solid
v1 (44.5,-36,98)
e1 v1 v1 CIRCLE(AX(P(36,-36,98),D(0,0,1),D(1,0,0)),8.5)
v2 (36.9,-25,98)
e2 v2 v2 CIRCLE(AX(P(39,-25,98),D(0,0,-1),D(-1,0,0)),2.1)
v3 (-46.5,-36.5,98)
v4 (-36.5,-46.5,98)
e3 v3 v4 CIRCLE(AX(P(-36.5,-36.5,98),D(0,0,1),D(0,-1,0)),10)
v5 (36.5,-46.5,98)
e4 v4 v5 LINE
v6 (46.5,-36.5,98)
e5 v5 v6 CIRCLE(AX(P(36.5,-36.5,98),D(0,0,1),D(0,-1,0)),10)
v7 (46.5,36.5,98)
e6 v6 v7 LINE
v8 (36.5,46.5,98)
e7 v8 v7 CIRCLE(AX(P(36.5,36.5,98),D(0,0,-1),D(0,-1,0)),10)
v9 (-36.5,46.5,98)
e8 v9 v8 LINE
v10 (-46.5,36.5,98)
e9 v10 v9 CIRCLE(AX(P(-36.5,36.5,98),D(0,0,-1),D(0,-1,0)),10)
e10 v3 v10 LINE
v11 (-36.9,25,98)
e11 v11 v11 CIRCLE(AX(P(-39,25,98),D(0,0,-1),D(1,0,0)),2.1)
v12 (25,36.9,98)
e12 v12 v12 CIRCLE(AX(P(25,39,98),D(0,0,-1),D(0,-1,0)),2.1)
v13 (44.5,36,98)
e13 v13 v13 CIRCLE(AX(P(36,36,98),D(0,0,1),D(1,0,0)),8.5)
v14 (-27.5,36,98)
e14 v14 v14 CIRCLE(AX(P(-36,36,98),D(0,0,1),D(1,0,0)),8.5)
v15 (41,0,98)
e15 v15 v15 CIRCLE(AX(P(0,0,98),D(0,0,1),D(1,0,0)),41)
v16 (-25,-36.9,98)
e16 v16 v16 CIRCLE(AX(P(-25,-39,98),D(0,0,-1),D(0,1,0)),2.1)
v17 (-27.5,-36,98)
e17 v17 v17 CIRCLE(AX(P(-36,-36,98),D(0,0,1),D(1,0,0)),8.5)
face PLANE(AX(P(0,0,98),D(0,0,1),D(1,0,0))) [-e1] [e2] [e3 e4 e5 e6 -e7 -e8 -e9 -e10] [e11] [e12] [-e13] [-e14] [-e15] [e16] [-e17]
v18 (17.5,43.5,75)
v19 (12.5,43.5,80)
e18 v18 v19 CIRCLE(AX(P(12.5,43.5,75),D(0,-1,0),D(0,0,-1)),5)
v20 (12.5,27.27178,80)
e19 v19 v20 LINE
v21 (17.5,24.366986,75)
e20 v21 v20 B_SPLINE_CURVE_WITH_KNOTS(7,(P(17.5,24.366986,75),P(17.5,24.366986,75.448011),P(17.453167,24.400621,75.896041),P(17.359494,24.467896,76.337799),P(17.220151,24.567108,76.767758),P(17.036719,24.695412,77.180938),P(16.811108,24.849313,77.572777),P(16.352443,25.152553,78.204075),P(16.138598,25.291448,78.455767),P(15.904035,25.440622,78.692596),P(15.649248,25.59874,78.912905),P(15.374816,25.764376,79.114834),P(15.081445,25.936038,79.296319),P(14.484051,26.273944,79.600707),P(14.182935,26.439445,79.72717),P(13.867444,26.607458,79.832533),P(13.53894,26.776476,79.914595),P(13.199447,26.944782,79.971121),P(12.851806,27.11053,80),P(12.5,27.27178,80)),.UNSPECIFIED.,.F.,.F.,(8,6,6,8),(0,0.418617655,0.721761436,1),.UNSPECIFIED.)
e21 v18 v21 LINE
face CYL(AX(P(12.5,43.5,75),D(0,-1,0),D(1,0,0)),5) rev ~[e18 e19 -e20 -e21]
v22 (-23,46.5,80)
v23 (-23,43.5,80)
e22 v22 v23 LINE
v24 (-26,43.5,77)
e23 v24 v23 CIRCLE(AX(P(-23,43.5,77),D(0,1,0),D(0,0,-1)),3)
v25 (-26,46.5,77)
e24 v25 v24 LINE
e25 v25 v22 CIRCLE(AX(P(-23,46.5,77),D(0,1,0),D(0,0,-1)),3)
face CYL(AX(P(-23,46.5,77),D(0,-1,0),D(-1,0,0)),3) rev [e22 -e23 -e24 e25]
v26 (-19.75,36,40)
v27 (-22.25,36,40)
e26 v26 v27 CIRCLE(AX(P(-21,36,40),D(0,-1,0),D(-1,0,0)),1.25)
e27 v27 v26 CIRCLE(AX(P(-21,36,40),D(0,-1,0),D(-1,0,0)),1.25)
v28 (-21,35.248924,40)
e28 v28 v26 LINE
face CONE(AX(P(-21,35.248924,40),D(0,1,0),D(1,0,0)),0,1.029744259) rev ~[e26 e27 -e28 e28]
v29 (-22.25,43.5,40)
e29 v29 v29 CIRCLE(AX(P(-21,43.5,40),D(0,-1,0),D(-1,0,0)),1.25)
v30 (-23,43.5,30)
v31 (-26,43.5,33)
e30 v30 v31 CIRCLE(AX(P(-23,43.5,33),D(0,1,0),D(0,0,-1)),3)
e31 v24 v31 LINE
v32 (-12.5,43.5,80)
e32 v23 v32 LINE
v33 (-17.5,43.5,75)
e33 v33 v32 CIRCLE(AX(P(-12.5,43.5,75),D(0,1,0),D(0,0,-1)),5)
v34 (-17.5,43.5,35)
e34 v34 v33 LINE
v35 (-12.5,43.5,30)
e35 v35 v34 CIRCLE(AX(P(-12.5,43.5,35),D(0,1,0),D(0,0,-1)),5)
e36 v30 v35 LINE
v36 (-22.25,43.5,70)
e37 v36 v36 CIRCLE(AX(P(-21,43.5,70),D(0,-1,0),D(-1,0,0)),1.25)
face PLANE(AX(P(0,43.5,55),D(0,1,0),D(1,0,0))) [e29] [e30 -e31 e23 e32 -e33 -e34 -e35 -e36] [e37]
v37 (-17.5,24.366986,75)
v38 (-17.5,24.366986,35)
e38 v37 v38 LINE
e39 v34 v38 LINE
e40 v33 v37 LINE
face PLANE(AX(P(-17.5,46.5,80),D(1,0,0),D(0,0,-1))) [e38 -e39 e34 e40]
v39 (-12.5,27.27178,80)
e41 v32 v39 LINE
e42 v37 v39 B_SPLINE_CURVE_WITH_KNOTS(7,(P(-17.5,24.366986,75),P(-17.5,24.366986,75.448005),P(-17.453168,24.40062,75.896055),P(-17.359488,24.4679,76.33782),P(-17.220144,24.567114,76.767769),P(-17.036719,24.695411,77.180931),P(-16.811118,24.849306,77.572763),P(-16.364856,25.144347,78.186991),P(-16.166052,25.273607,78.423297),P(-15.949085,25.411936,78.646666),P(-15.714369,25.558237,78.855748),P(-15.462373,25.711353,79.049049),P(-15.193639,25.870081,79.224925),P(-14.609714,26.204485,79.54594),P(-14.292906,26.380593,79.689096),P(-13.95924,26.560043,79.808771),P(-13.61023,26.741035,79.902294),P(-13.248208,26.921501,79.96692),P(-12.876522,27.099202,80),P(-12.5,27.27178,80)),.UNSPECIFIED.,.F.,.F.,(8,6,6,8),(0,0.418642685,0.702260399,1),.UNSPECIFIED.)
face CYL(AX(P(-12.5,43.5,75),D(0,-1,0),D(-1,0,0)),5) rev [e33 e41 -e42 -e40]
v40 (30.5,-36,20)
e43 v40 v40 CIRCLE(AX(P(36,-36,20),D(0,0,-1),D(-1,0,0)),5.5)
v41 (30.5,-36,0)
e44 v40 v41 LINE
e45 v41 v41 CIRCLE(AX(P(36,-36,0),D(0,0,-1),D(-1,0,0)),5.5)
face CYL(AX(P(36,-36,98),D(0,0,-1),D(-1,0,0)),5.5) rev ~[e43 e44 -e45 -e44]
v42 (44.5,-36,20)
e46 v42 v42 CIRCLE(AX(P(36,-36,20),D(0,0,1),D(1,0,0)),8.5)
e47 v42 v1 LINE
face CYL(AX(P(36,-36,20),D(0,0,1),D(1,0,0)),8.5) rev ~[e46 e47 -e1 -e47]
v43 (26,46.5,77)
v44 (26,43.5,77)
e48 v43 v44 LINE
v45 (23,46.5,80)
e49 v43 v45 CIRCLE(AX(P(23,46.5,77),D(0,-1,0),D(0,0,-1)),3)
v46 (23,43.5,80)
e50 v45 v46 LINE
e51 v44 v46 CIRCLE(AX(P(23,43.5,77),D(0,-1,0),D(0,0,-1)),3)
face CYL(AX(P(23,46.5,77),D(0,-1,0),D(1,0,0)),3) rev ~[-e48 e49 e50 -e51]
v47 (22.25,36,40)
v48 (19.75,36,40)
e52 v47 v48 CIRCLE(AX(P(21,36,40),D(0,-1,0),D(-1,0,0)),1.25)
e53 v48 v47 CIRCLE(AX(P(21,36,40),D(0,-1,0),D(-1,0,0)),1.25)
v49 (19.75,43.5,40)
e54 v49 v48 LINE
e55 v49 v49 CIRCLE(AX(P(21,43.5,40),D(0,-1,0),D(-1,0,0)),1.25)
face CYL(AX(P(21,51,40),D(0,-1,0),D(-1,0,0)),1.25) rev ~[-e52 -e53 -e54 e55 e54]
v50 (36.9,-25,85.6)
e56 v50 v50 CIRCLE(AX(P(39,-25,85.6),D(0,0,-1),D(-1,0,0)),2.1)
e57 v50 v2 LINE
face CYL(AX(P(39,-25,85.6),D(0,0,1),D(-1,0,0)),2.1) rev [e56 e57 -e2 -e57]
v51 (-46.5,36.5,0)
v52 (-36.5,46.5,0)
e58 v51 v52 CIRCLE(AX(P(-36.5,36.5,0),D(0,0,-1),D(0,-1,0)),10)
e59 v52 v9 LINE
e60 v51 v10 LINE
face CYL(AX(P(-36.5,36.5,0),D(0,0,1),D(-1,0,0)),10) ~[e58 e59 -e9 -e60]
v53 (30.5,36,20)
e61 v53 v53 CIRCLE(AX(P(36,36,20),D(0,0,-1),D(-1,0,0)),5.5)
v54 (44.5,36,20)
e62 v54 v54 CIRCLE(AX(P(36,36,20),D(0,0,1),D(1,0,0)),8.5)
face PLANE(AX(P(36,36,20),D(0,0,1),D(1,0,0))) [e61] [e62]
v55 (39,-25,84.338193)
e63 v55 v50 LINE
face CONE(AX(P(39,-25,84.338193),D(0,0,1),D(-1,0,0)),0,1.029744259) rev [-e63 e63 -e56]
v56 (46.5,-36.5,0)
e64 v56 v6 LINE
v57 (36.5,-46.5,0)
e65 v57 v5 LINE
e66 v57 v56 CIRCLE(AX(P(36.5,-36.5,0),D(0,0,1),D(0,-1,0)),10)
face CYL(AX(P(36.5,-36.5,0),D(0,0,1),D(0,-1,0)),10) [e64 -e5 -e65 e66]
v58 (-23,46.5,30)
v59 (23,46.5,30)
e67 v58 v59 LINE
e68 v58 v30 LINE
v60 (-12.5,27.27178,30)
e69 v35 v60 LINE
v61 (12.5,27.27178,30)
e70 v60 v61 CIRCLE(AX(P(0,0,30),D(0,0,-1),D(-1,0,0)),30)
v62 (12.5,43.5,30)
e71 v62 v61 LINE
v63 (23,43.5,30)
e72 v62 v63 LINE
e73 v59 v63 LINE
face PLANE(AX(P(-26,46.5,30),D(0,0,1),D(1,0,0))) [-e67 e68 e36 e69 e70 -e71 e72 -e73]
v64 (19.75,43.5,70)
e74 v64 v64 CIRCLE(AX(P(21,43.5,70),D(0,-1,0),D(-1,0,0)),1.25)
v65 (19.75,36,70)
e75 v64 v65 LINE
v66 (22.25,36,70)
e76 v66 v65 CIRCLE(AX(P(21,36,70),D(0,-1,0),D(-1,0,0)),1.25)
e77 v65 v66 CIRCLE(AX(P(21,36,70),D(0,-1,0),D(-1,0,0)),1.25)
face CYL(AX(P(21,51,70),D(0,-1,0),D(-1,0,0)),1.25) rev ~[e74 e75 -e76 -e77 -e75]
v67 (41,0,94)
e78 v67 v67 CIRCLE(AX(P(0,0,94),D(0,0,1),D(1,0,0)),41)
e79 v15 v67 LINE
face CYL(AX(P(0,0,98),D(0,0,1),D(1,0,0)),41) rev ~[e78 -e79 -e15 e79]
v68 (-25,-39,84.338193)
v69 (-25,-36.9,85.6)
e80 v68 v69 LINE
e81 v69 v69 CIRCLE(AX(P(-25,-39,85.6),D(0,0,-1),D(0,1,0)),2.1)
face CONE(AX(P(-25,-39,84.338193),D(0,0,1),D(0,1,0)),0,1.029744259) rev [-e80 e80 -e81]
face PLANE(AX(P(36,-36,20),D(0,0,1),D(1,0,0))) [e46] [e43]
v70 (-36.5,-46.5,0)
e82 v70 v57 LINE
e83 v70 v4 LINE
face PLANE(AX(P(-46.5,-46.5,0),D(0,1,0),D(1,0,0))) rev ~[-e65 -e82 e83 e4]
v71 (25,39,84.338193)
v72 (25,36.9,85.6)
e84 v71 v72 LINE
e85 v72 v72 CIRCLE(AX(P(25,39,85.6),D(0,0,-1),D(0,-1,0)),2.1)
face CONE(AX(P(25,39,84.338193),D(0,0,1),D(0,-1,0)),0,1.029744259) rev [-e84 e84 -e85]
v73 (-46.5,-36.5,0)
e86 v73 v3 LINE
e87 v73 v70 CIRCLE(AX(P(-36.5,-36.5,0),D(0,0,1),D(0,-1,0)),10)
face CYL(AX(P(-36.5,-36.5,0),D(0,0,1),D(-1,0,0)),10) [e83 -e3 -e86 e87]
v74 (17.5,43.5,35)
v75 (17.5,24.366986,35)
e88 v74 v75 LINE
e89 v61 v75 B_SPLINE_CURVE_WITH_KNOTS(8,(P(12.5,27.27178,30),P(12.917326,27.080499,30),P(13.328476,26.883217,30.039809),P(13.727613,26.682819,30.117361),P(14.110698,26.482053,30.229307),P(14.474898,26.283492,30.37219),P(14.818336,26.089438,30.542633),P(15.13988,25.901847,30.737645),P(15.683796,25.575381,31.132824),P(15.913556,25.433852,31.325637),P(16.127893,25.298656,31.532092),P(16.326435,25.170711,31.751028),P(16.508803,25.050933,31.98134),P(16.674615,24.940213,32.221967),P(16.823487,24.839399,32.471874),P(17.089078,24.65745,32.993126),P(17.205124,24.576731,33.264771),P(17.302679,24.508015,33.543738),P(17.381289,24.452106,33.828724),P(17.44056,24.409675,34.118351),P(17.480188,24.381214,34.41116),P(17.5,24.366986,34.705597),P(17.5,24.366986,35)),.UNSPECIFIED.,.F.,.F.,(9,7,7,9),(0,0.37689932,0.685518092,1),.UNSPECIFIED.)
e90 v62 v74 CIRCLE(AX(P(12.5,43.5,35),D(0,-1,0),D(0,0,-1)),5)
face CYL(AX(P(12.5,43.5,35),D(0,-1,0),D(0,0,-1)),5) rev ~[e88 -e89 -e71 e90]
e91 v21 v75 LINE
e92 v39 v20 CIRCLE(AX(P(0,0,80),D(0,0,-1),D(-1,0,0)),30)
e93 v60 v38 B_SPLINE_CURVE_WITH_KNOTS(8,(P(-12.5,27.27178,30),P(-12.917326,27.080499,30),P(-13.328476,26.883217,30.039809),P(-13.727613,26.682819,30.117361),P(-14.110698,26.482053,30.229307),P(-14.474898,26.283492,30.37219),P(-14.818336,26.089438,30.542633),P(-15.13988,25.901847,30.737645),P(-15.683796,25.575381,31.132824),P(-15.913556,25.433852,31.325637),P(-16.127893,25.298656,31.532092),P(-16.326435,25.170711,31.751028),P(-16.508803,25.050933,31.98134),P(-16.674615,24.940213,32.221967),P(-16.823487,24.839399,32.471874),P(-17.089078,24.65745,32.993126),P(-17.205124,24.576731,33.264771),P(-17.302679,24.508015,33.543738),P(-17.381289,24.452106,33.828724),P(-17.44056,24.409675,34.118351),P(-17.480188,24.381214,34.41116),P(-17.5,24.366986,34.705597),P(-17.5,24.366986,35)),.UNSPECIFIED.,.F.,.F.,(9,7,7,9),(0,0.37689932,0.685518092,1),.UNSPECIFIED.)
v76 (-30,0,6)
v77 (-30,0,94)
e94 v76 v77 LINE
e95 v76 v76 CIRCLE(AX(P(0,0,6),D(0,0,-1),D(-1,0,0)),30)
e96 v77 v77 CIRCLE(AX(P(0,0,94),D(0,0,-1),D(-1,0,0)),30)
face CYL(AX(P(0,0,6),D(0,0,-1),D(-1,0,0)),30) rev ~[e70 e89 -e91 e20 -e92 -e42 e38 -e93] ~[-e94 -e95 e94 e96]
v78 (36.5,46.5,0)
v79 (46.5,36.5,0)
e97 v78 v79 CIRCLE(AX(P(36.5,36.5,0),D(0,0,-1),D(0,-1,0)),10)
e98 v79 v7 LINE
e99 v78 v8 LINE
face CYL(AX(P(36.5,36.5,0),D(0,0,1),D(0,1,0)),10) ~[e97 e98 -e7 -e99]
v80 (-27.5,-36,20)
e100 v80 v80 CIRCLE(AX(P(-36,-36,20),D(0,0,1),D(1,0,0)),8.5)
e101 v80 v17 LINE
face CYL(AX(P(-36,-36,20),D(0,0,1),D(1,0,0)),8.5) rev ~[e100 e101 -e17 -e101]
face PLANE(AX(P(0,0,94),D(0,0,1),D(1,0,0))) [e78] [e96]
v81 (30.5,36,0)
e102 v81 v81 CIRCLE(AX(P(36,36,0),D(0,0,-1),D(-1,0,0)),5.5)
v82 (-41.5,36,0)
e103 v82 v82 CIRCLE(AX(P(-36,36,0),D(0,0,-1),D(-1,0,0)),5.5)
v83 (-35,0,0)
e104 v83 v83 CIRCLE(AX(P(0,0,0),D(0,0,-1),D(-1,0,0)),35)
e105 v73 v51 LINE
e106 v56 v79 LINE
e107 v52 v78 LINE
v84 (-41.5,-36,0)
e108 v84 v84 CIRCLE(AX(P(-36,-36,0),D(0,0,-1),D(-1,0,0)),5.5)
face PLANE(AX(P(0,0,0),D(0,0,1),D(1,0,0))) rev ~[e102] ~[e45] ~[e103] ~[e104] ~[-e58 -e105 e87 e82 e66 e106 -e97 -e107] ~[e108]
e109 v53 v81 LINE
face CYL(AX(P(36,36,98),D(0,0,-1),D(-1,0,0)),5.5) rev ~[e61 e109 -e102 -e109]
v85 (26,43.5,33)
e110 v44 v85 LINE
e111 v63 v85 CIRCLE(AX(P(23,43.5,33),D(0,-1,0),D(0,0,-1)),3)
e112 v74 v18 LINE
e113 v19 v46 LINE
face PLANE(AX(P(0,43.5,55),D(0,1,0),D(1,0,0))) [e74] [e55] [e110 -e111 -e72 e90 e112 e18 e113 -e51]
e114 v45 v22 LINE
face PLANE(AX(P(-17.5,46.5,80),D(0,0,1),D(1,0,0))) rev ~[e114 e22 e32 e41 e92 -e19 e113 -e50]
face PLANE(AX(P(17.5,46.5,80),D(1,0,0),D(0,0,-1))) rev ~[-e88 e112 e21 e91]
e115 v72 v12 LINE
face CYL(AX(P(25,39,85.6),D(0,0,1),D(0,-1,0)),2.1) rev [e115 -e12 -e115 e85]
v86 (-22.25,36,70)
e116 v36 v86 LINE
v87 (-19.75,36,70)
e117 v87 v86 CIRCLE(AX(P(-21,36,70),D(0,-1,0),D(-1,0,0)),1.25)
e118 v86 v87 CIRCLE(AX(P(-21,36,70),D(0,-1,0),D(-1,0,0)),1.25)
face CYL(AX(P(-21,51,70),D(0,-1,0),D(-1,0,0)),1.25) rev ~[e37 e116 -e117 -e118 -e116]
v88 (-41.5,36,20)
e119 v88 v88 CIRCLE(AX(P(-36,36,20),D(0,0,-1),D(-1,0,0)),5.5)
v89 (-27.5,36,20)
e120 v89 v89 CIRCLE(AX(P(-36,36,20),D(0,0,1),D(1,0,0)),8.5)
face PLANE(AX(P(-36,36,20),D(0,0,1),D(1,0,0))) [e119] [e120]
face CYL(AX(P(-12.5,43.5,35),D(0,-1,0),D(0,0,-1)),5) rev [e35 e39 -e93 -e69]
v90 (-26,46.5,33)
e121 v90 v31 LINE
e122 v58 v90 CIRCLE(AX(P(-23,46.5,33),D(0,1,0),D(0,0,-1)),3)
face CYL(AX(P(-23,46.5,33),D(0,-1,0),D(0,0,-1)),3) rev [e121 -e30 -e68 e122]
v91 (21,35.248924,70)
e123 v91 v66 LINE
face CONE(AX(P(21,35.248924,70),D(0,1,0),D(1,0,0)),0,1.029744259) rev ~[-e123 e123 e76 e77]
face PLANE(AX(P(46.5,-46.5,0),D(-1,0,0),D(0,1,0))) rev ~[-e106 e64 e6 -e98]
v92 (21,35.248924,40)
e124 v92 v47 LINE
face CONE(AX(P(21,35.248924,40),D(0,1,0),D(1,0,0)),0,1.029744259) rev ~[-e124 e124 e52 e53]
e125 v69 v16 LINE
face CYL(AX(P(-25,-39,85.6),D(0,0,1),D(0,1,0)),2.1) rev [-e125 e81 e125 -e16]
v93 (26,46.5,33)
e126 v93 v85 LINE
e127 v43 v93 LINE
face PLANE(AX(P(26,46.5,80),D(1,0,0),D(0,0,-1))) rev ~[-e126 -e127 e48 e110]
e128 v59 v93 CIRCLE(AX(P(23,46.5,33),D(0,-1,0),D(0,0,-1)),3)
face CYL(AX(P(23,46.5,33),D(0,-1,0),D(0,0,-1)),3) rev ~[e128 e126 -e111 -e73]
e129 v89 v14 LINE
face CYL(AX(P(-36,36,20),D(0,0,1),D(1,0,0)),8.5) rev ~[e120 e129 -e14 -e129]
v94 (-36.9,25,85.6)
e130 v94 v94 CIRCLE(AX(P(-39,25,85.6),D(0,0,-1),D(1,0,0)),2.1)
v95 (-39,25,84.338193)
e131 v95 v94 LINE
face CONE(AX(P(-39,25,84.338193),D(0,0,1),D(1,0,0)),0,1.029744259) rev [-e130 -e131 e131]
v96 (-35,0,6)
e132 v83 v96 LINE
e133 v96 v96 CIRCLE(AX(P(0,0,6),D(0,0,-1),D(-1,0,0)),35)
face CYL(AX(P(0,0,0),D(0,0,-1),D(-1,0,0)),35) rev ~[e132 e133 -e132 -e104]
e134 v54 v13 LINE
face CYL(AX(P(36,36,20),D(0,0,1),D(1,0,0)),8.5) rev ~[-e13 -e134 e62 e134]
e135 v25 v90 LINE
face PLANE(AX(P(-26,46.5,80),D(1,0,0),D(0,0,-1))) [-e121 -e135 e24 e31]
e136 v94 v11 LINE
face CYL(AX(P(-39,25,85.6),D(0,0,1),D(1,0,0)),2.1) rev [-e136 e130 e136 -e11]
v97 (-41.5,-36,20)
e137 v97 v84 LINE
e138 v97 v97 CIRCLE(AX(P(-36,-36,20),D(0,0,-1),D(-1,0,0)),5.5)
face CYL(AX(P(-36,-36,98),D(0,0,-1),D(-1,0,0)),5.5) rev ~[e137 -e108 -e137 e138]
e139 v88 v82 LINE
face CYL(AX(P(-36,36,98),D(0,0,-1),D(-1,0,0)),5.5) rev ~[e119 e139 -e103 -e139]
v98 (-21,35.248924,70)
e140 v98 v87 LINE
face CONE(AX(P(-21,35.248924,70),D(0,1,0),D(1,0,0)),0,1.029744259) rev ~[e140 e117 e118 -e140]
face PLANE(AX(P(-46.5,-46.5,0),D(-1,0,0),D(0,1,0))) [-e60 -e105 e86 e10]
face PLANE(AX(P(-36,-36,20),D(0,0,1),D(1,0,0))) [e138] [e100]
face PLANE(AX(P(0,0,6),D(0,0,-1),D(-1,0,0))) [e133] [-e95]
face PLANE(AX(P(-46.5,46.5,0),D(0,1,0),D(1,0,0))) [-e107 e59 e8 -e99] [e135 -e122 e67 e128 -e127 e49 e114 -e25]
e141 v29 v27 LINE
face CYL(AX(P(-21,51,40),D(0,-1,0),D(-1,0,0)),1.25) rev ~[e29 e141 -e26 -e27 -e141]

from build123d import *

# Parameters (mm, degrees)
SKETCH1_W                                = 93
SKETCH1_H                                = 93
BOSS_EXTRUDE1_DEPTH                      = 98
SKETCH2_R                                = 35
CUT_EXTRUDE1_DEPTH                       = 6
SKETCH3_R                                = 30
CUT_EXTRUDE2_DEPTH                       = 114.086250269
CUT_EXTRUDE3_REACH                       = 144.882
CUT_EXTRUDE3_END_RADIUS                  = 30
SKETCH4_W                                = 35
SKETCH4_H                                = 50
FILLET1_R                                = 10
CBORE_FOR_M10_HEX_HEAD_BOLT1_D           = 11
CBORE_FOR_M10_HEX_HEAD_BOLT1_CBORE_D     = 17
CBORE_FOR_M10_HEX_HEAD_BOLT1_CBORE_DEPTH = 78
SKETCH9_R                                = 41
CUT_EXTRUDE4_DEPTH                       = 4
SKETCH10_W                               = 52
SKETCH10_H                               = 50
CUT_EXTRUDE5_DEPTH                       = 3
FILLET2_R                                = 3
M3_TAPPED_HOLE1_D                        = 2.5
M3_TAPPED_HOLE1_DEPTH                    = 7.5
M3_TAPPED_HOLE1_TIP                      = 0.751075774
FILLET3_R                                = 5
CIRPATTERN1_COUNT                        = 4


with BuildPart() as part:
    # Sketch1 → Boss-Extrude1 (new body)
    with BuildSketch(Plane.XY):
        Rectangle(SKETCH1_W, SKETCH1_H)
    extrude(amount=BOSS_EXTRUDE1_DEPTH)

    # Sketch2 → Cut-Extrude1 (cut)
    with BuildSketch(Plane(origin=(0, 0, 0), x_dir=(-1, 0, 0), z_dir=(0, 0, -1))):
        Circle(SKETCH2_R)
    extrude(amount=-CUT_EXTRUDE1_DEPTH, mode=Mode.SUBTRACT)

    # Sketch3 → Cut-Extrude2 (cut, through all)
    with BuildSketch(Plane(origin=(0, 0, 6), x_dir=(-1, 0, 0), z_dir=(0, 0, -1))):
        Circle(SKETCH3_R)
    extrude(amount=-CUT_EXTRUDE2_DEPTH, mode=Mode.SUBTRACT)

    # Cut-Extrude3: up to this cylinder (the profile starts outside it)
    cut_extrude3_end = Plane(origin=(0, 0, 55), z_dir=(0, 0, -1)) * Cylinder(CUT_EXTRUDE3_END_RADIUS, 350.764, mode=Mode.PRIVATE)
    # Sketch4 → Cut-Extrude3 (cut, up to the surface)
    with BuildSketch(Plane(origin=(0, 46.5, 0), x_dir=(1, 0, 0), z_dir=(0, 1, 0)), mode=Mode.PRIVATE) as cut_extrude3_sk1:
        with Locations((0, -55)):
            Rectangle(SKETCH4_W, SKETCH4_H)
    cut_extrude3_tool1 = extrude(cut_extrude3_sk1.sketch, amount=-CUT_EXTRUDE3_REACH, mode=Mode.PRIVATE) - cut_extrude3_end
    add(cut_extrude3_tool1.solids().sort_by_distance((0, 46.5, 55))[0], mode=Mode.SUBTRACT)

    # Fillet1
    fillet1_edges = [part.edges().sort_by_distance(p)[0] for p in [
        (46.5, -46.5, 49),
        (-46.5, -46.5, 49),
        (-46.5, 46.5, 49),
        (46.5, 46.5, 49),
    ]]
    fillet(fillet1_edges, radius=FILLET1_R)

    # CBORE for M10 Hex Head Bolt1 (through all)
    with Locations(Plane.XY.offset(98)):
        with Locations((-36, 36), (36, 36), (36, -36), (-36, -36)):
            CounterBoreHole(CBORE_FOR_M10_HEX_HEAD_BOLT1_D / 2, CBORE_FOR_M10_HEX_HEAD_BOLT1_CBORE_D / 2, CBORE_FOR_M10_HEX_HEAD_BOLT1_CBORE_DEPTH)

    # Sketch9 → Cut-Extrude4 (cut)
    with BuildSketch(Plane.XY.offset(98)):
        Circle(SKETCH9_R)
    extrude(amount=-CUT_EXTRUDE4_DEPTH, mode=Mode.SUBTRACT)

    # Sketch10 → Cut-Extrude5 (cut)
    with BuildSketch(Plane(origin=(0, 46.5, 0), x_dir=(1, 0, 0), z_dir=(0, 1, 0))):
        with Locations((0, -55)):
            Rectangle(SKETCH10_W, SKETCH10_H)
    extrude(amount=-CUT_EXTRUDE5_DEPTH, mode=Mode.SUBTRACT)

    # Fillet2
    fillet2_edges = [part.edges().sort_by_distance(p)[0] for p in [
        (26, 45, 80),
        (-26, 45, 30),
        (26, 45, 30),
        (-26, 45, 80),
    ]]
    fillet(fillet2_edges, radius=FILLET2_R)

    # M3 Tapped Hole1
    with Locations(Plane(origin=(0, 43.5, 0), x_dir=(1, 0, 0), z_dir=(0, 1, 0))):
        with Locations((21, -40), (21, -70), (-21, -70), (-21, -40)):
            Hole(M3_TAPPED_HOLE1_D / 2, depth=M3_TAPPED_HOLE1_DEPTH)
            with Locations((0, 0, -(M3_TAPPED_HOLE1_DEPTH + M3_TAPPED_HOLE1_TIP / 2))):  # 118° drill point
                Cone(0, M3_TAPPED_HOLE1_D / 2, M3_TAPPED_HOLE1_TIP, mode=Mode.SUBTRACT)

    # Fillet3
    fillet3_edges = [part.edges().sort_by_distance(p)[0] for p in [
        (17.5, 33.933492931, 30),
        (17.5, 33.933492931, 80),
        (-17.5, 33.933492931, 80),
        (-17.5, 33.933492931, 30),
    ]]
    fillet(fillet3_edges, radius=FILLET3_R)

    # Sketch14 → M5 Tapped Hole2 (revolve, cut)
    with BuildSketch(Plane(origin=(25, 39, 98), x_dir=(0, -1, 0), z_dir=(1, 0, 0))):
        Polygon((0, 0), (0, 13.6618073), (2.1, 12.4), (2.1, 0), align=None)
    m5_tapped_hole2 = revolve(axis=Axis((25, 39, 104.35), (0, 0, -1)), mode=Mode.SUBTRACT)

    # CirPattern1: M5 Tapped Hole2 ×4 about axis
    cirpattern1_axis = Axis((0, 0, 0), (0, 0, 1))
    for i in range(1, CIRPATTERN1_COUNT):
        add(m5_tapped_hole2.rotate(cirpattern1_axis, i * 360 / CIRPATTERN1_COUNT), mode=Mode.SUBTRACT)


solid = part.part
